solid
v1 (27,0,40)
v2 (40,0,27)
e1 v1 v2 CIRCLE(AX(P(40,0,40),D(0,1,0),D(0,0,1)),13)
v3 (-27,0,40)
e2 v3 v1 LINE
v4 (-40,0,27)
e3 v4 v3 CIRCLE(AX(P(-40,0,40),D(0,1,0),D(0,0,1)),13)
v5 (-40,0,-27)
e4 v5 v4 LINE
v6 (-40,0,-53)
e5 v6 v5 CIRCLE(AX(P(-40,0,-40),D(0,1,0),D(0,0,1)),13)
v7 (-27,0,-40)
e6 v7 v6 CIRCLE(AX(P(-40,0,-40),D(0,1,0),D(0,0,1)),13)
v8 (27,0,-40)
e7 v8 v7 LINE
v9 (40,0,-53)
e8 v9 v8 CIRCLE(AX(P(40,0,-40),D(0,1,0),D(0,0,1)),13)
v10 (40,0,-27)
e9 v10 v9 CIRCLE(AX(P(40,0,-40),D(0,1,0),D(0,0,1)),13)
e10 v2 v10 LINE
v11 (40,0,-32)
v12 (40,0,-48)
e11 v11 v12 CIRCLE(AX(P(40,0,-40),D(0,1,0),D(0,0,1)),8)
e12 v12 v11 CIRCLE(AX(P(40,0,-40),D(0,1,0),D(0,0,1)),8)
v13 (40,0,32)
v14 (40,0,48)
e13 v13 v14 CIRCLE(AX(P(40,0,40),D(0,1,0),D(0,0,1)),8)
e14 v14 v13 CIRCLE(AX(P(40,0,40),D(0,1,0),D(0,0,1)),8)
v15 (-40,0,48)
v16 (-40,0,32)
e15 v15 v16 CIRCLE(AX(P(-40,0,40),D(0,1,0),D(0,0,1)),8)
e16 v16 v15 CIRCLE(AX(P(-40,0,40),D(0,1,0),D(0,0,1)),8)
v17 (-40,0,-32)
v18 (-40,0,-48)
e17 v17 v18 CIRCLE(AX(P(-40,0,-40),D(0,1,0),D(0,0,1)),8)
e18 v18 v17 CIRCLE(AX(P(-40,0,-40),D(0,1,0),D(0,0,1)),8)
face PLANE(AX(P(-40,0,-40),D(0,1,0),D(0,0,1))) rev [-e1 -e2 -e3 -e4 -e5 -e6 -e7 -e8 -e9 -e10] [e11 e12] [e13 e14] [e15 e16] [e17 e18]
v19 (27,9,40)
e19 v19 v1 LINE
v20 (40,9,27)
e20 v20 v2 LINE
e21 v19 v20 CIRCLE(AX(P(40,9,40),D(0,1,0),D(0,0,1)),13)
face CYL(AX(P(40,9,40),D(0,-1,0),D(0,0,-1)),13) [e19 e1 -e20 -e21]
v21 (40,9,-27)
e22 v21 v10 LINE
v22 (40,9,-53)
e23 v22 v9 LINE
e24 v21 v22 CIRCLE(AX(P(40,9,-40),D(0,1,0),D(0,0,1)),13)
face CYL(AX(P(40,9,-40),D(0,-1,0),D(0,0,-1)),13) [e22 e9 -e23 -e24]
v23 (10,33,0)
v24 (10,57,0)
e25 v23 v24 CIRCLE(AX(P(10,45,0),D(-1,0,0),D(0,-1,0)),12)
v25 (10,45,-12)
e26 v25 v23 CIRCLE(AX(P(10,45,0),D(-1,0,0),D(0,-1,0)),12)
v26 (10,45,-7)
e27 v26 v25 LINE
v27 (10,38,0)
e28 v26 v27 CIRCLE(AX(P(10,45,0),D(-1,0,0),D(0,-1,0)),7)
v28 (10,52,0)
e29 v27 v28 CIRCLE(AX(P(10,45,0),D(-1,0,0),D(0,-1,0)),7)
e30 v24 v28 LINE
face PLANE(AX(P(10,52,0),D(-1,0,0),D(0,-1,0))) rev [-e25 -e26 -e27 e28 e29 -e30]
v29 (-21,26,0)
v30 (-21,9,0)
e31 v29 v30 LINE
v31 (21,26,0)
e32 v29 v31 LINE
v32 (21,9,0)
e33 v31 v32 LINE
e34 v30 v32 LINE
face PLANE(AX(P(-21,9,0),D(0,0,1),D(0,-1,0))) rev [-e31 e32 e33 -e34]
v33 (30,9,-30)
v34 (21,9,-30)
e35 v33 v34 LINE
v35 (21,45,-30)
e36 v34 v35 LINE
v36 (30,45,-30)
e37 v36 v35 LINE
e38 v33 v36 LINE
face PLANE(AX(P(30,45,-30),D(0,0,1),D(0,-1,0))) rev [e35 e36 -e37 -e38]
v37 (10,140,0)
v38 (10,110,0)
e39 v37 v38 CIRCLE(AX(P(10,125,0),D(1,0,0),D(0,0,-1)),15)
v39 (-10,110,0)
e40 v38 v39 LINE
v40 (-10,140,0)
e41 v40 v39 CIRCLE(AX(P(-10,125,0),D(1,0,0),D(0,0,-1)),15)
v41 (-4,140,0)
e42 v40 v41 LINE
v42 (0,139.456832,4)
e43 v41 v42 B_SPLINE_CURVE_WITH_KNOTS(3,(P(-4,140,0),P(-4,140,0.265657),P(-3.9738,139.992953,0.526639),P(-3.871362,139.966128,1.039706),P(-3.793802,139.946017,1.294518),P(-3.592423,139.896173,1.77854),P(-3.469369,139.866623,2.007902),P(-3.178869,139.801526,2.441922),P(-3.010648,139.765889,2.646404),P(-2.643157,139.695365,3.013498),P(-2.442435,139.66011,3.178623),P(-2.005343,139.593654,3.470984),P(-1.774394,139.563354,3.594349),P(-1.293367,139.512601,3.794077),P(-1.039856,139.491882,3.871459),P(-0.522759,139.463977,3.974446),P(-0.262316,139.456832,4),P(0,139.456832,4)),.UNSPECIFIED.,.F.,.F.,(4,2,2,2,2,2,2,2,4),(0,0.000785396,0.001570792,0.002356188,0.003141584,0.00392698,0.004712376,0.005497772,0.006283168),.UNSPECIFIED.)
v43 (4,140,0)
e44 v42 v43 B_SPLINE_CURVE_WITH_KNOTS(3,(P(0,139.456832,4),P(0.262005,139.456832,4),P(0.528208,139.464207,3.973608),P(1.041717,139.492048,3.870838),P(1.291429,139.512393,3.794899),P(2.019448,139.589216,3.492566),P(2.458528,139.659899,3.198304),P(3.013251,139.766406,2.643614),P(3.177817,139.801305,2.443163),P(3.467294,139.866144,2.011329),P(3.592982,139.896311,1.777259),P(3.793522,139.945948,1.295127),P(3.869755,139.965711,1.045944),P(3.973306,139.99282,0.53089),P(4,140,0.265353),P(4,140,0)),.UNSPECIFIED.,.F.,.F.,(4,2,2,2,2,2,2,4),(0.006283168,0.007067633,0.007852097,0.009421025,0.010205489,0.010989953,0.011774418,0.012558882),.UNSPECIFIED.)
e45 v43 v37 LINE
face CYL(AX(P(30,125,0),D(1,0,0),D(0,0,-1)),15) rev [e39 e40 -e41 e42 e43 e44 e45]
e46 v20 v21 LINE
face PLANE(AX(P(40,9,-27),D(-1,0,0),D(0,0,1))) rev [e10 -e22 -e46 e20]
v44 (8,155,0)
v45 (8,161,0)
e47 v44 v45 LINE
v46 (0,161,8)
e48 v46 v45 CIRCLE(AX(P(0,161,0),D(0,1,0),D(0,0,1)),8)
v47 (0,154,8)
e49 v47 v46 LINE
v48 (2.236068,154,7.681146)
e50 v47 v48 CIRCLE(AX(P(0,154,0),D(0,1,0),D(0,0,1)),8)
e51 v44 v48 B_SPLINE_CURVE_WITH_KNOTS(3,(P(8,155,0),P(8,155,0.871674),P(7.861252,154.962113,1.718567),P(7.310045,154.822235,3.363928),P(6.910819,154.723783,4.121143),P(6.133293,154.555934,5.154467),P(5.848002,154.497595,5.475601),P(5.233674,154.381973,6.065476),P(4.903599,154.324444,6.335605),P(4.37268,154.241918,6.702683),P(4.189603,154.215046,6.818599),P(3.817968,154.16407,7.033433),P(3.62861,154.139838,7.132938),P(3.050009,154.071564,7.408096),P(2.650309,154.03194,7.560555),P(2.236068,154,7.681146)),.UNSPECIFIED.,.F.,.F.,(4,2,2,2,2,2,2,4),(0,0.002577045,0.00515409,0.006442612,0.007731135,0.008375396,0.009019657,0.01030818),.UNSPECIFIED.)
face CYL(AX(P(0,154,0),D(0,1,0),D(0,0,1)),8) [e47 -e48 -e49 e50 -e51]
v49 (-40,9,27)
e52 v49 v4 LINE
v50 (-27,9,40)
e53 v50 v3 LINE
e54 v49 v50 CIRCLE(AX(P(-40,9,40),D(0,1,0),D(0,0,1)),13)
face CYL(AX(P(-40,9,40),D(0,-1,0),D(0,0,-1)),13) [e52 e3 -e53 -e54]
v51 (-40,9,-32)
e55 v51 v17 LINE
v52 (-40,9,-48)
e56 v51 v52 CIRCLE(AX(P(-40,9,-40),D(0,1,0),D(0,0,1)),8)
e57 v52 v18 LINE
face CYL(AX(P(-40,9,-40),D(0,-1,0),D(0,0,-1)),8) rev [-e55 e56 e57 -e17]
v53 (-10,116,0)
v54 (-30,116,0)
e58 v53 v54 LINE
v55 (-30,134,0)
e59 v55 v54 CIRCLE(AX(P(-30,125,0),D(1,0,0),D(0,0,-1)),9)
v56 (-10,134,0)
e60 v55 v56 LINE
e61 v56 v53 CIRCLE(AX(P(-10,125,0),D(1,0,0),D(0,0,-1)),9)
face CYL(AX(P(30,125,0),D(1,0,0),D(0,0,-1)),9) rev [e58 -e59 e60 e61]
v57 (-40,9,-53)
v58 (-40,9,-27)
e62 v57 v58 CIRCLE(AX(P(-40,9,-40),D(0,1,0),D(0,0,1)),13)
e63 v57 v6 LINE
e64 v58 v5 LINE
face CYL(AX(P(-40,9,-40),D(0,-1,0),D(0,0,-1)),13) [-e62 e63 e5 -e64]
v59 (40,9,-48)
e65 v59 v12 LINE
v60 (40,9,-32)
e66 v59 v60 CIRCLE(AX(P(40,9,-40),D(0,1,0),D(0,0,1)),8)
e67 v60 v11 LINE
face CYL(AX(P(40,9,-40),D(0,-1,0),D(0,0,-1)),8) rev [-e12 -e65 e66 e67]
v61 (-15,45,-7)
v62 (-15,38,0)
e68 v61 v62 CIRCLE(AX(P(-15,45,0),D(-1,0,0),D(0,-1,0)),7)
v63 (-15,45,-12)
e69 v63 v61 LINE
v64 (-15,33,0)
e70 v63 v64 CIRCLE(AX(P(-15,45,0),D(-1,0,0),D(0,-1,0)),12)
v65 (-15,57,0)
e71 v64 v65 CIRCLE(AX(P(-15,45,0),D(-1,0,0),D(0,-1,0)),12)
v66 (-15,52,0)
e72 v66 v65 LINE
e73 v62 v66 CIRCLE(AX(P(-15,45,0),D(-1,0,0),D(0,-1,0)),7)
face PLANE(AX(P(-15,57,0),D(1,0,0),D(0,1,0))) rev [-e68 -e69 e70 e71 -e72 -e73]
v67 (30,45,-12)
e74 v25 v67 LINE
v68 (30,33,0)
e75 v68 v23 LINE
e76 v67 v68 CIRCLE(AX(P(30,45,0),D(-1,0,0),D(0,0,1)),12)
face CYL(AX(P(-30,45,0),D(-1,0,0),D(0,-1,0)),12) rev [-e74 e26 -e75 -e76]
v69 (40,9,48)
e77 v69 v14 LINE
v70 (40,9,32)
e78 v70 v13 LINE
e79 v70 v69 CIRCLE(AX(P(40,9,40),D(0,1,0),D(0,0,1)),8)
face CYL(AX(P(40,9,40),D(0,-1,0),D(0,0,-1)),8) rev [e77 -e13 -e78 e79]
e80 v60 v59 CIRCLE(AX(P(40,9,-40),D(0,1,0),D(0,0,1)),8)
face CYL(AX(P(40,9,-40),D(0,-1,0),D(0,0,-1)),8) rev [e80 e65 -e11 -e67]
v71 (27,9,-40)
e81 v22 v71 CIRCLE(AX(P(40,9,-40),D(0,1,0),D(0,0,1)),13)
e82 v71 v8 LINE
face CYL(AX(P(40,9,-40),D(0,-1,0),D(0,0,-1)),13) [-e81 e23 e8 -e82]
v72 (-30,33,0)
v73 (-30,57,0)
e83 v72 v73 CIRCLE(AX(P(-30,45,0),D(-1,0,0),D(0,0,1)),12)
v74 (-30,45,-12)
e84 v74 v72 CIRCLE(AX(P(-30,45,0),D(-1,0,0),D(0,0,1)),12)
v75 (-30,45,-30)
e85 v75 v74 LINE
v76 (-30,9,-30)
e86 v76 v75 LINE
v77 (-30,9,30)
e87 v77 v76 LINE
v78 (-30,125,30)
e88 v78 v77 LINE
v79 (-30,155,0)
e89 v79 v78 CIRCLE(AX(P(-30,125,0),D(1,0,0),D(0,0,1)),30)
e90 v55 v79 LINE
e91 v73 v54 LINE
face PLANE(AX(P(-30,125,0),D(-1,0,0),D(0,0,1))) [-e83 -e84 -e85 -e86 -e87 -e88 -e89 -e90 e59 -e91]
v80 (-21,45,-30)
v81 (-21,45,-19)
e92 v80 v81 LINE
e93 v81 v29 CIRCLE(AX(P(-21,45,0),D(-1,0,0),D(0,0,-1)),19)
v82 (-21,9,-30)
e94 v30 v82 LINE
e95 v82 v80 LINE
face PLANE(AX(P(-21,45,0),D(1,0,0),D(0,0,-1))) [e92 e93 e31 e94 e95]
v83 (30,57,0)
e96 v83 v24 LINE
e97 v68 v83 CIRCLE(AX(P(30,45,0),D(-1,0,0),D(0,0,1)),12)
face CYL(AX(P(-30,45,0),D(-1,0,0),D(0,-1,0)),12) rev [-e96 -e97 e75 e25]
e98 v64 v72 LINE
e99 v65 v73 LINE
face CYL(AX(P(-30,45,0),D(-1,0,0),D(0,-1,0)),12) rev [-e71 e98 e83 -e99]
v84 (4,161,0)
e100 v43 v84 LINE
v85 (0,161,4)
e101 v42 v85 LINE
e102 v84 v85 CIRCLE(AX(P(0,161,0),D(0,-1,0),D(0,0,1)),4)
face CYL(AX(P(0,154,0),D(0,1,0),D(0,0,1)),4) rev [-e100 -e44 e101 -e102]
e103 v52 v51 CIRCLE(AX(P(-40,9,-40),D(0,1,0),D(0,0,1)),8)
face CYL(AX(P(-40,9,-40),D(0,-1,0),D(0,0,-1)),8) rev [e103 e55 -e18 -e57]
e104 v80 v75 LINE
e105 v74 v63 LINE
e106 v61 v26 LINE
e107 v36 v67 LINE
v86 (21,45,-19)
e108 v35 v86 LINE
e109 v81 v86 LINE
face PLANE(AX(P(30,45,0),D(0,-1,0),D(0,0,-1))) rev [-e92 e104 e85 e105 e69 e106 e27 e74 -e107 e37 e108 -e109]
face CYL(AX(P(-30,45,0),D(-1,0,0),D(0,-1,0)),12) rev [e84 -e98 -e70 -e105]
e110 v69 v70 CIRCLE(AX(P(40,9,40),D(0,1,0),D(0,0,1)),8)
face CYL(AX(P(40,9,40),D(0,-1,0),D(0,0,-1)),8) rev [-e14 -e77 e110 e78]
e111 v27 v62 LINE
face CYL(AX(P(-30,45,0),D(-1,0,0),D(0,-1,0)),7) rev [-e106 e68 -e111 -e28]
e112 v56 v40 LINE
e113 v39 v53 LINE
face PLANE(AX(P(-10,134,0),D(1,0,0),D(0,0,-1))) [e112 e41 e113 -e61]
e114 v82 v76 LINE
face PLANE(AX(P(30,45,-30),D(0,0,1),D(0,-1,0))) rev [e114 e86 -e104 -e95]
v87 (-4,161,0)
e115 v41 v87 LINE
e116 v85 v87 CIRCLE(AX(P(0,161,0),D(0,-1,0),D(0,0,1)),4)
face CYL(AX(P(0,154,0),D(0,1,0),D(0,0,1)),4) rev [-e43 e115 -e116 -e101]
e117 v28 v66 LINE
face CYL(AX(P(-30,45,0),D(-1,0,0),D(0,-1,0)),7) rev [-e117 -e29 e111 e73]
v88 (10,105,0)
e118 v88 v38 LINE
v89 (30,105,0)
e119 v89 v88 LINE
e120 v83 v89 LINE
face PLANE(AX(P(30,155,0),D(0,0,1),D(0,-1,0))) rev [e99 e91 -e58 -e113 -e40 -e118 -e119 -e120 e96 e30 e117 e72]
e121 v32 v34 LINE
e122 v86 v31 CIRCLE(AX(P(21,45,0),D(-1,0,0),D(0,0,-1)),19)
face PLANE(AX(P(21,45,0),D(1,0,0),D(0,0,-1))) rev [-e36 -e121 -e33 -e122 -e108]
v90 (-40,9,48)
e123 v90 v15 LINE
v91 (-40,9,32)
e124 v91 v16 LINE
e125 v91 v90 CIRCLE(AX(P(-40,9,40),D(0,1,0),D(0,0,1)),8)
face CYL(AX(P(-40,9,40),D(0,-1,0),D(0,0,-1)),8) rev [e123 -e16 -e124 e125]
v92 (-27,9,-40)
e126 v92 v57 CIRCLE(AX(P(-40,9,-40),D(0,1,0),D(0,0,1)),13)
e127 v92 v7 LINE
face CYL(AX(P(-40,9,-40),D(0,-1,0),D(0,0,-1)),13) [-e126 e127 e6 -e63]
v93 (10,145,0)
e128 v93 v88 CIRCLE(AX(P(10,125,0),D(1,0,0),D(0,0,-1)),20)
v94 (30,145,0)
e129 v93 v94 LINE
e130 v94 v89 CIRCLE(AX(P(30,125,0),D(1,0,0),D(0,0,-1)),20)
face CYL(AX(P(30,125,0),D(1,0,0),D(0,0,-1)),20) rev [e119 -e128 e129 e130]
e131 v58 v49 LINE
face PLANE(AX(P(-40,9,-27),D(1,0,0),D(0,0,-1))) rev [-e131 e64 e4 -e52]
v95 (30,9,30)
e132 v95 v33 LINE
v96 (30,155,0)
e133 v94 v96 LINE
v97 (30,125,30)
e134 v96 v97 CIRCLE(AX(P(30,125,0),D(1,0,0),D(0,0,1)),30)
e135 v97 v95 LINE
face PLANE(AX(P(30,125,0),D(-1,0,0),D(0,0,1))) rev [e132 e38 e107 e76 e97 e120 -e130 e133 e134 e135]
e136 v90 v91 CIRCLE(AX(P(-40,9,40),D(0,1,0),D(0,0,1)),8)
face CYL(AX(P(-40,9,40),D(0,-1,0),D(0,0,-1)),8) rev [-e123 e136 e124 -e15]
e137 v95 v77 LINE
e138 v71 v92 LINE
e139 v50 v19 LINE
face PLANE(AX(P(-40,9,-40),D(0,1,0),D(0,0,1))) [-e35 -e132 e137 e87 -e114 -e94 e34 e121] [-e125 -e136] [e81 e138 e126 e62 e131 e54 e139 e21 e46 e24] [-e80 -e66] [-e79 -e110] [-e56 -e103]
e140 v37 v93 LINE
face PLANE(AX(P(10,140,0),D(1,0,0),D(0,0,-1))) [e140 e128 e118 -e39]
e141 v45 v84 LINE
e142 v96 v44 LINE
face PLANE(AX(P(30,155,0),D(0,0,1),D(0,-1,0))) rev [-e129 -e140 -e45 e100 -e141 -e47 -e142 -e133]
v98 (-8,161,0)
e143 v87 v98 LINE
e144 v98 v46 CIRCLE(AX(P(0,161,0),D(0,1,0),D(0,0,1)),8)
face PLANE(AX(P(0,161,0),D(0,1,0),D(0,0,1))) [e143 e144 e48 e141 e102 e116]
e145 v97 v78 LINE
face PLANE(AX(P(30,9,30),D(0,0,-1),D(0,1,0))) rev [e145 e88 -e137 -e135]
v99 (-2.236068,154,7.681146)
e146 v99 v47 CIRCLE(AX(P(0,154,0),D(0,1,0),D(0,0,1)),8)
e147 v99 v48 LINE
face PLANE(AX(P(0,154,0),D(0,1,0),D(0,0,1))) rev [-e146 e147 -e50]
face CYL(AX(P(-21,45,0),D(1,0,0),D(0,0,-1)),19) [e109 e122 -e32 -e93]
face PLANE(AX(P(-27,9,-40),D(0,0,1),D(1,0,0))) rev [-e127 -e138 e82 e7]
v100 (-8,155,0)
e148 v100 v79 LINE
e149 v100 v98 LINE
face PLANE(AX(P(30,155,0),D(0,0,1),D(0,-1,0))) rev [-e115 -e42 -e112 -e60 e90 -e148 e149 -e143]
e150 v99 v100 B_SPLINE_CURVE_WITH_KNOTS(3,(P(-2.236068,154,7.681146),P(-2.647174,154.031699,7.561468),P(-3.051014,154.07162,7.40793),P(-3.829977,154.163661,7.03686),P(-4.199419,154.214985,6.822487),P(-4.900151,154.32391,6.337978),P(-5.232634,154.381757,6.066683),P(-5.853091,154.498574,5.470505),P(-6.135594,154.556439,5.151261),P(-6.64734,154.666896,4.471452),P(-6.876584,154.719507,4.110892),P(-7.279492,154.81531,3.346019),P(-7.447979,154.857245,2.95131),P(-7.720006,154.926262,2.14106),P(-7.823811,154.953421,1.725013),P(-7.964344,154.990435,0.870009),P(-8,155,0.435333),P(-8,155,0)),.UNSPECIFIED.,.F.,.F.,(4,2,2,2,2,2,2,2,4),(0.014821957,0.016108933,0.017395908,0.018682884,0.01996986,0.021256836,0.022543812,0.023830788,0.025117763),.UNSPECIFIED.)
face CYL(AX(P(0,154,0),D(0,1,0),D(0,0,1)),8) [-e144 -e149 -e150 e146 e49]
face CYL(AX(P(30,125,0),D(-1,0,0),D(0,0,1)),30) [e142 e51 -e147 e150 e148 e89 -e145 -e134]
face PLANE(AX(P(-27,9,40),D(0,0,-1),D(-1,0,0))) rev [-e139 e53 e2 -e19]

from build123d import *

# Parameters (mm, degrees)
BASE_FLANGE_SKETCH_R = 8
BASE_FLANGE_DEPTH    = 9
TOWER_DEPTH          = 30
SIDE_SLOT_DEPTH      = 21
CLIP_BOSS_DEPTH      = 6
CLIP_BOSS_DEPTH_BACK = 1
CLIP_SLOT_REACH      = 174.171
CLIP_SLOT_END_RADIUS = 15


with BuildPart() as part:
    # Base Flange Sketch → Base Flange (new body)
    with BuildSketch(Plane(origin=(0, 0, 0), x_dir=(1, 0, 0), z_dir=(0, 1, 0))):
        with BuildLine():
            Line((-27, 40), (27, 40))
            ThreePointArc((27, 40), (49.192388155, 49.192388155), (40, 27))
            Line((40, 27), (40, -27))
            ThreePointArc((40, -27), (49.192388155, -49.192388155), (27, -40))
            Line((27, -40), (-27, -40))
            ThreePointArc((-27, -40), (-49.192388155, -49.192388155), (-40, -27))
            Line((-40, -27), (-40, 27))
            ThreePointArc((-40, 27), (-49.192388155, 49.192388155), (-27, 40))
        make_face()
        with Locations(Location((-40, 40, 0), (0, 0, 270))):
            Circle(BASE_FLANGE_SKETCH_R, mode=Mode.SUBTRACT)
        with Locations(Location((40, 40, 0), (0, 0, 270))):
            Circle(BASE_FLANGE_SKETCH_R, mode=Mode.SUBTRACT)
        with Locations(Location((40, -40, 0), (0, 0, 270))):
            Circle(BASE_FLANGE_SKETCH_R, mode=Mode.SUBTRACT)
        with Locations(Location((-40, -40, 0), (0, 0, 270))):
            Circle(BASE_FLANGE_SKETCH_R, mode=Mode.SUBTRACT)
    extrude(amount=BASE_FLANGE_DEPTH)

    # Tower Profile Sketch → Tower (add, symmetric)
    with BuildSketch(Plane(origin=(0, 0, 0), x_dir=(0, 0, -1), z_dir=(1, 0, 0))):
        with BuildLine():
            Line((-30, 9), (-30, 125))
            ThreePointArc((-30, 125), (-21.213203436, 146.213203436), (0, 155))
            Line((0, 155), (0, 45))
            Line((0, 45), (30, 45))
            Line((30, 45), (30, 9))
            Line((30, 9), (-30, 9))
        make_face()
    extrude(amount=TOWER_DEPTH, both=True)

    # Lower Bore Profile Sketch → Lower Bore (revolve, cut)
    with BuildSketch(Plane(origin=(0, 0, 0), x_dir=(-1, 0, 0), z_dir=(0, 0, -1))):
        Polygon((30, 134), (10, 134), (10, 140), (-10, 140), (-10, 145), (-30, 145), (-30, 125), (30, 125), align=None)
    revolve(axis=Axis((30, 125, 0), (-1, 0, 0)), mode=Mode.SUBTRACT)

    # Upper Bore Profile Sketch → Upper Bore (revolve, cut)
    with BuildSketch(Plane(origin=(0, 0, 0), x_dir=(-1, 0, 0), z_dir=(0, 0, -1))):
        Polygon((30, 57), (15, 57), (15, 52), (-10, 52), (-10, 57), (-30, 57), (-30, 45), (30, 45), align=None)
    revolve(axis=Axis((-30, 45, 0), (1, 0, 0)), mode=Mode.SUBTRACT)

    # Side Slot Sketch → Side Slot (cut, symmetric)
    with BuildSketch(Plane(origin=(0, 0, 0), x_dir=(0, 0, -1), z_dir=(1, 0, 0))):
        with BuildLine():
            Line((19, 45), (30, 45))
            Line((30, 45), (30, 9))
            Line((30, 9), (0, 9))
            Line((0, 9), (0, 26))
            ThreePointArc((0, 26), (13.435028843, 31.564971157), (19, 45))
        make_face()
    extrude(amount=SIDE_SLOT_DEPTH, both=True, mode=Mode.SUBTRACT)

    # Clip Boss Sketch → Clip Boss (add, two sides: drawn at the far end of the back side and taken through both)
    with BuildSketch(Plane(origin=(0, 155, 0), x_dir=(1, 0, 0), z_dir=(0, 1, 0)).offset(-CLIP_BOSS_DEPTH_BACK)):
        with BuildLine():
            Line((-8, 0), (-4, 0))
            ThreePointArc((-4, 0), (0, -4), (4, 0))
            Line((4, 0), (8, 0))
            ThreePointArc((8, 0), (0, -8), (-8, 0))
        make_face()
    extrude(amount=CLIP_BOSS_DEPTH + CLIP_BOSS_DEPTH_BACK)

    # Clip Slot: up to this cylinder (the profile starts outside it)
    clip_slot_end = Plane(origin=(0, 125, 0), z_dir=(1, 0, 0)) * Cylinder(CLIP_SLOT_END_RADIUS, 379.342, mode=Mode.PRIVATE)
    # Clip Slot Sketch → Clip Slot (cut, up to the surface)
    with BuildSketch(Plane(origin=(0, 155, 0), x_dir=(1, 0, 0), z_dir=(0, 1, 0)), mode=Mode.PRIVATE) as clip_slot_sk1:
        with BuildLine():
            Line((-4, 0), (4, 0))
            ThreePointArc((4, 0), (0, -4), (-4, 0))
        make_face()
    clip_slot_tool1 = extrude(clip_slot_sk1.sketch, amount=-CLIP_SLOT_REACH, mode=Mode.PRIVATE) - clip_slot_end
    add(clip_slot_tool1.solids().sort_by_distance((0, 155, 1.697653))[0], mode=Mode.SUBTRACT)


solid = part.part
